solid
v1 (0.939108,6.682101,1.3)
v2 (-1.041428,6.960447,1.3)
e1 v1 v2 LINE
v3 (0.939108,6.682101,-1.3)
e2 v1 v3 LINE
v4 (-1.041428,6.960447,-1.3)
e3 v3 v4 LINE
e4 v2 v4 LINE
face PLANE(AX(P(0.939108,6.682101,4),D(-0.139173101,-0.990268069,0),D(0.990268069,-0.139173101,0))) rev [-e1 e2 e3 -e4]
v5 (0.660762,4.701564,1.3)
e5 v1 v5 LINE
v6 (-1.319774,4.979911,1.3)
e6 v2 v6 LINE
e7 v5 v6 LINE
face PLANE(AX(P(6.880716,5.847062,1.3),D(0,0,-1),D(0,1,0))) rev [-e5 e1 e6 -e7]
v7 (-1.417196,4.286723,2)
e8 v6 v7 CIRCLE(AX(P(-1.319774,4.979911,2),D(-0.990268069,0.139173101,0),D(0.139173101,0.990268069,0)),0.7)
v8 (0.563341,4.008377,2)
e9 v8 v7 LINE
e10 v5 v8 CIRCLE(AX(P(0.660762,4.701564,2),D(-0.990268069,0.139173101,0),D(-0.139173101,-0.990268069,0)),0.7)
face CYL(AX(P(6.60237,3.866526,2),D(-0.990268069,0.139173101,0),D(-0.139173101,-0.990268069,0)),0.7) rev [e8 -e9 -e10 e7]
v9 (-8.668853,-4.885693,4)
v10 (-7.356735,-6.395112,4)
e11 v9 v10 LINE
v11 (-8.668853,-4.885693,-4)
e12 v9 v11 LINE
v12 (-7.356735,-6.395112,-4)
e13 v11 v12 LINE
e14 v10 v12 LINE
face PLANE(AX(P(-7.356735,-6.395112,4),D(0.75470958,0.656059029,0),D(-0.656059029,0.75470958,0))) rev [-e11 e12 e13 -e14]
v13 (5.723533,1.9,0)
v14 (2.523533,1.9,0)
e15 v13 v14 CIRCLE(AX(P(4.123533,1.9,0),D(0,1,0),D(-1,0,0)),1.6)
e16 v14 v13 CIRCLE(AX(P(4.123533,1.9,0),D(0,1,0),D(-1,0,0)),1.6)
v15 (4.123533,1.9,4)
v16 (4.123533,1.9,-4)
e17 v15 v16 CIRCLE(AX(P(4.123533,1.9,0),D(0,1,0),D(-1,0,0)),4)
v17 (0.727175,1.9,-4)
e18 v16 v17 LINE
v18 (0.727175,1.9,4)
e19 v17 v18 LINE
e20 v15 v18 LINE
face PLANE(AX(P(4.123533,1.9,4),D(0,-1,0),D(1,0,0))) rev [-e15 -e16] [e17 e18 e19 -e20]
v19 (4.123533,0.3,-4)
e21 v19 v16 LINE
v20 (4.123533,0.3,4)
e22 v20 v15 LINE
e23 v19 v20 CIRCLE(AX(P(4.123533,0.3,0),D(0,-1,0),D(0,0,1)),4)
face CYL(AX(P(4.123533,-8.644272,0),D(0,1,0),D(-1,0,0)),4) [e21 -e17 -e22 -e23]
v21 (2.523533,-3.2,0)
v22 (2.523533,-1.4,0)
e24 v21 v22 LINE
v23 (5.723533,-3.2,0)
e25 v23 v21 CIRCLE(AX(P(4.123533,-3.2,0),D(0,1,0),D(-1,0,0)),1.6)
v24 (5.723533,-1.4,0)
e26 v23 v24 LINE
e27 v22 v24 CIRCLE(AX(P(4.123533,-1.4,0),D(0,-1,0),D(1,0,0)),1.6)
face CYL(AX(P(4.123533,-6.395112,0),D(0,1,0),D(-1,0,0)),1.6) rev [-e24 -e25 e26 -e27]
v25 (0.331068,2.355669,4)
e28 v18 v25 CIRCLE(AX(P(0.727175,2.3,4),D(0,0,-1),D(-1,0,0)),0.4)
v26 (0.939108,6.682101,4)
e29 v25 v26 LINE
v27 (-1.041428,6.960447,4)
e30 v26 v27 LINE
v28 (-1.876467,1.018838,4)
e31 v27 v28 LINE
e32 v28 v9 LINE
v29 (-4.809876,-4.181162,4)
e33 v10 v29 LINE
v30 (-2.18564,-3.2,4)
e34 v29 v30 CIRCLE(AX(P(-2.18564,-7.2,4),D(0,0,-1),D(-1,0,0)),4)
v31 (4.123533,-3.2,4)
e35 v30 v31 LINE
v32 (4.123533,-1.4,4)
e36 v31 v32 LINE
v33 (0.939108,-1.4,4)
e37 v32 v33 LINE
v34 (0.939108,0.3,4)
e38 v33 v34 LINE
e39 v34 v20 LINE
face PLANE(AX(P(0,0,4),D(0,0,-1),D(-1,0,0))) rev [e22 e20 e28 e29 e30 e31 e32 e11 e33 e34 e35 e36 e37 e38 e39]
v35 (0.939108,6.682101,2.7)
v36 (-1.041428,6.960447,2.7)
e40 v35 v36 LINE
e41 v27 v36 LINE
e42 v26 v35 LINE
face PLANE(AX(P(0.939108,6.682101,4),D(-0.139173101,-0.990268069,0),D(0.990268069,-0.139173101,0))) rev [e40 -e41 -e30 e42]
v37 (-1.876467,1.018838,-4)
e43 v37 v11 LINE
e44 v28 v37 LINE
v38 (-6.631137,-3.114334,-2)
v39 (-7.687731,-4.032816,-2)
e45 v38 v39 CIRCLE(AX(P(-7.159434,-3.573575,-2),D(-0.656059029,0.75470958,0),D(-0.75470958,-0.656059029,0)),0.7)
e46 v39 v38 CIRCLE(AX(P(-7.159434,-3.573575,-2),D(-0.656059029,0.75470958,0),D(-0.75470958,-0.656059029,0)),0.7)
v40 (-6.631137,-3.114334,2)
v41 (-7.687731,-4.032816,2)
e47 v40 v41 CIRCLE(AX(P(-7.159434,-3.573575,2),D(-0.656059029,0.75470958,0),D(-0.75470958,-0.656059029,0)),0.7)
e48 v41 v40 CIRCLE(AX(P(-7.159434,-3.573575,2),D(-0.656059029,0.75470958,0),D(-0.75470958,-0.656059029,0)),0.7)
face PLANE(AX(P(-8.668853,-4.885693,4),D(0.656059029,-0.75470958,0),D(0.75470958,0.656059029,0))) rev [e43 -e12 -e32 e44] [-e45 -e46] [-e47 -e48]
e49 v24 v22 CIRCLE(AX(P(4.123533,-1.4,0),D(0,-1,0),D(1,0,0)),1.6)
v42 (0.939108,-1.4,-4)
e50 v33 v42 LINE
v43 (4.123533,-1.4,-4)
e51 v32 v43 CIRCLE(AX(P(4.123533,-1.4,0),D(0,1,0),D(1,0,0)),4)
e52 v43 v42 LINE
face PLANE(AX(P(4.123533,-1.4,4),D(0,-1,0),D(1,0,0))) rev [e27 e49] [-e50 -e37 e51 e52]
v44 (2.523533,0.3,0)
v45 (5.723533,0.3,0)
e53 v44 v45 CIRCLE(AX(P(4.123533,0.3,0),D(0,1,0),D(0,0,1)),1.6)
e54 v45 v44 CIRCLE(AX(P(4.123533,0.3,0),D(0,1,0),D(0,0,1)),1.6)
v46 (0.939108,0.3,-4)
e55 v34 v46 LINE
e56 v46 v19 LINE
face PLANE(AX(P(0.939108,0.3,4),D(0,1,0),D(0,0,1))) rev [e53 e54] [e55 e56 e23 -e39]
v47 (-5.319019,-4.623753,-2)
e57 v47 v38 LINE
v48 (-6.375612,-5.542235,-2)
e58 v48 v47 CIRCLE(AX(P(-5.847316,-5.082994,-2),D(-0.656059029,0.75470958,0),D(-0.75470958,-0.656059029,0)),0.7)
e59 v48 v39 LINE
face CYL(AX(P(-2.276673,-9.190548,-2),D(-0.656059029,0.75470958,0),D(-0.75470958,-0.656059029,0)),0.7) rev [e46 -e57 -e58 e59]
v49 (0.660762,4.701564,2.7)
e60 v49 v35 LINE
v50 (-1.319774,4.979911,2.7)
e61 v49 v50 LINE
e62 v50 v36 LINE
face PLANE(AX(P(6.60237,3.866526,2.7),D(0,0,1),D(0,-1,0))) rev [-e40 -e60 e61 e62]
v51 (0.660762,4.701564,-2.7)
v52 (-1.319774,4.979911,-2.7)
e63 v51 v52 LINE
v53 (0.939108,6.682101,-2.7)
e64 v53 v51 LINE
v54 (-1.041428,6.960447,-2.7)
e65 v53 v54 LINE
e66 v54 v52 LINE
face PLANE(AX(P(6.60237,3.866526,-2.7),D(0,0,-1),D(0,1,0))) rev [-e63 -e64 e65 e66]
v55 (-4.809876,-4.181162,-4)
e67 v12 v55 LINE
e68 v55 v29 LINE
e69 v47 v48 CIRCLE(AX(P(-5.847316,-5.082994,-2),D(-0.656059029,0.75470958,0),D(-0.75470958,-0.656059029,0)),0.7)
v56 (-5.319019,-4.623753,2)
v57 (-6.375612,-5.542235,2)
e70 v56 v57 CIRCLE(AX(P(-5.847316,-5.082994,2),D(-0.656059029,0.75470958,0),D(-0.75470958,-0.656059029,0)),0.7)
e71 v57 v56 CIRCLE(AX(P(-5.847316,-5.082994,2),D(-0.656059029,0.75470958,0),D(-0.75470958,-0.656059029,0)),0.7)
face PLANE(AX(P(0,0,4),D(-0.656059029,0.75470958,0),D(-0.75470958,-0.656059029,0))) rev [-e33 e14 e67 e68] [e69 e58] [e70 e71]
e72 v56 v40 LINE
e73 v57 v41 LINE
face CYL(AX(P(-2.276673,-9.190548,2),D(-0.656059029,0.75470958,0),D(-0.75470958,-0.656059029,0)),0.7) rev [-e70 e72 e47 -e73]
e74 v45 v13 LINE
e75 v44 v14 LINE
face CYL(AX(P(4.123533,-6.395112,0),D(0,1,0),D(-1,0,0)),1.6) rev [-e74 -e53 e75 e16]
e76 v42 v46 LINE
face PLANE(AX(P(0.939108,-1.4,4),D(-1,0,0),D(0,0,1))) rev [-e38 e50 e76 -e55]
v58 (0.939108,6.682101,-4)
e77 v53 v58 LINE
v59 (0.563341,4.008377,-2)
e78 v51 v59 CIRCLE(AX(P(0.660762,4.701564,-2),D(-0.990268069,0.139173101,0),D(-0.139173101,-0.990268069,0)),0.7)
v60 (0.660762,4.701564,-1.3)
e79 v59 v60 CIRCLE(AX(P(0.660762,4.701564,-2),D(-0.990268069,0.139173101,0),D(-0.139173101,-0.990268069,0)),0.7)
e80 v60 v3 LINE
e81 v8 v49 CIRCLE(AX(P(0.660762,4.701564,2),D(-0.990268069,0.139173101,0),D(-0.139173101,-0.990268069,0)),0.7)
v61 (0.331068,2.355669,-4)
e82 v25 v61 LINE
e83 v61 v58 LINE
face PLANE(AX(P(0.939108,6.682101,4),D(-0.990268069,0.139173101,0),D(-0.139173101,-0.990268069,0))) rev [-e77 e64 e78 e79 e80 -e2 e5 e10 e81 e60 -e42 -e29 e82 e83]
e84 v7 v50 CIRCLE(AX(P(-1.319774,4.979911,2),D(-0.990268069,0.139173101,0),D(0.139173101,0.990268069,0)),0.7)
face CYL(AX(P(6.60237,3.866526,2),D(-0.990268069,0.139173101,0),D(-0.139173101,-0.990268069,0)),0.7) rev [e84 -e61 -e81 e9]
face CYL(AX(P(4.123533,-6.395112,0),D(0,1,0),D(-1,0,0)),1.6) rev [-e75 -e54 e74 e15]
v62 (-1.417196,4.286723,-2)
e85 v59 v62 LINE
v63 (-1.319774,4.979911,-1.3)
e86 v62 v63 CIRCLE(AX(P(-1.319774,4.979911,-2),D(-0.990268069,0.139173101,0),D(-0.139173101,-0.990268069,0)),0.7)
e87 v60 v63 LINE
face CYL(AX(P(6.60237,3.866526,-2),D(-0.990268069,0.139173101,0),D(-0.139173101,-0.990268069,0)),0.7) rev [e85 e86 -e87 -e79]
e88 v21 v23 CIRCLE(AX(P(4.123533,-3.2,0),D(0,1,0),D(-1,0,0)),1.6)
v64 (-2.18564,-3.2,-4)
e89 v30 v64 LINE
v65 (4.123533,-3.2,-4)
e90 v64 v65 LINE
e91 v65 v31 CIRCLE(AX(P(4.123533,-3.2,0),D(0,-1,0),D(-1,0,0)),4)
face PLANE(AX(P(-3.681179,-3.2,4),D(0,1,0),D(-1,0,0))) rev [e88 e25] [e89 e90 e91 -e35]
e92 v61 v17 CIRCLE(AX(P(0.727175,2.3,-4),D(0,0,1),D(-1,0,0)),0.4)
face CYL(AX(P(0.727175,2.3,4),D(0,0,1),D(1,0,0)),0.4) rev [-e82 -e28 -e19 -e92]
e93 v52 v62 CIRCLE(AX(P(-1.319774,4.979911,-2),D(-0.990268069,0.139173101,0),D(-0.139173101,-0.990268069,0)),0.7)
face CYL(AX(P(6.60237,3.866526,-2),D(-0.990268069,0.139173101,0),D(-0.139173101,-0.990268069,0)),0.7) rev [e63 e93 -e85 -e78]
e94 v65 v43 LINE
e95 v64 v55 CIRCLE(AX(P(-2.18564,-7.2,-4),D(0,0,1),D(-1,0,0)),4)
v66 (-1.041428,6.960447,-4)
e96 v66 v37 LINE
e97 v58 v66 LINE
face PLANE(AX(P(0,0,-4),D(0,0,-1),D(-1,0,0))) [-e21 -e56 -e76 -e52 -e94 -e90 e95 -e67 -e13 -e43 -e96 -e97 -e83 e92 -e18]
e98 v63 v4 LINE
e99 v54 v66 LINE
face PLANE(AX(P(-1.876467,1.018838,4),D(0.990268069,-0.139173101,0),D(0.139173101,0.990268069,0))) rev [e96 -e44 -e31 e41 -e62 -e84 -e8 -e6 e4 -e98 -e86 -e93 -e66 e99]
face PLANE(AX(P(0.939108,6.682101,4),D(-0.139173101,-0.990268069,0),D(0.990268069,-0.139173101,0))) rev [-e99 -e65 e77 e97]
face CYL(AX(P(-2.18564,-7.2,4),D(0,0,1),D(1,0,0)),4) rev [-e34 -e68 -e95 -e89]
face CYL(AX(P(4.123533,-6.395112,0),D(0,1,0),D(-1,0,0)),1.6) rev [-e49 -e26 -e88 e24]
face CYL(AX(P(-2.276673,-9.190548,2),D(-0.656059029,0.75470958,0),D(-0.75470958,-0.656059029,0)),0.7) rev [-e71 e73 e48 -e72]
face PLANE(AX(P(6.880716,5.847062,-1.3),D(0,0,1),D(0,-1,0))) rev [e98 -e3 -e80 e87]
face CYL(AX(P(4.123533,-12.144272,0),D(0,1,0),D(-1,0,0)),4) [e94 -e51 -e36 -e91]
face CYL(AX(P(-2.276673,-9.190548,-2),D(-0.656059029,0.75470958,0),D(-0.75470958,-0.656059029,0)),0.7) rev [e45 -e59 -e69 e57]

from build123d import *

# Parameters (mm, degrees)
BASE_ARM_8MM_DEPTH   = 4
FINGER_SLOTS_DEPTH   = 8
SIDE_SLOT_PROFILE_R  = 0.7
SIDE_SLOT_DEPTH      = 12.515344682
CLEVIS_LUG_8MM_DEPTH = 4
LUG_END_ROUND_R4_R   = 4
EDGE_FILLET_R0_4_R   = 0.4
LUG_FILL_BOSS_DEPTH  = 1.8
LUG_BLEND_BOSS_DEPTH = 1.6
PIN_HOLE_PROFILE_R   = 1.6
PIN_HOLE_3_2_DEPTH   = 13.647446253


with BuildPart() as part:
    # Base Arm Profile → Base Arm 8mm (new, symmetric)
    with BuildSketch(Plane.XY):
        Polygon((0, 0), (-7.356734921, -6.3951121), (-8.668852979, -4.88569294), (-1.876466757, 1.018838321), (-1.041428151, 6.960446733), (0.939107986, 6.682100531), align=None)
    extrude(amount=BASE_ARM_8MM_DEPTH, both=True)

    # Finger Slots Profile → Finger Slots (cut)
    with BuildSketch(Plane(origin=(-1.980536137, 0.278346202, 0), x_dir=(0, 0, 1), z_dir=(-0.9902680687415697, 0.13917310096006985, 0))):
        with BuildLine():
            Line((-2.7, 4.747769359), (-2.7, 6.747769359))
            Line((-2.7, 6.747769359), (-1.3, 6.747769359))
            Line((-1.3, 6.747769359), (-1.3, 4.747769359))
            ThreePointArc((-1.3, 4.747769359), (-2, 4.047769359), (-2.7, 4.747769359))
        make_face()
        with BuildLine():
            Line((1.3, 6.747769359), (1.3, 4.747769359))
            ThreePointArc((1.3, 4.747769359), (2, 4.047769359), (2.7, 4.747769359))
            Line((2.7, 4.747769359), (2.7, 6.747769359))
            Line((2.7, 6.747769359), (1.3, 6.747769359))
        make_face()
    extrude(amount=-FINGER_SLOTS_DEPTH, mode=Mode.SUBTRACT)

    # Side Slot Profile → Side Slot (cut, through all)
    with BuildSketch(Plane(origin=(-1.312118058, 1.50941916, 0), x_dir=(0.7547095802227755, 0.6560590289905035, 0), z_dir=(-0.6560590289905035, 0.7547095802227755, 0))):
        with Locations(Location((-7.747769359, -2, 0), (0, 0, 180))):
            Circle(SIDE_SLOT_PROFILE_R)
        with Locations(Location((-7.747769359, 2, 0), (0, 0, 180))):
            Circle(SIDE_SLOT_PROFILE_R)
    extrude(amount=-SIDE_SLOT_DEPTH, mode=Mode.SUBTRACT)

    # Clevis Lug Profile → Clevis Lug 8mm (add, symmetric)
    with BuildSketch(Plane.XY):
        Polygon((-3.681178903, -3.2), (4.123533243, -3.2), (4.123533243, -1.4), (0.939107986, -1.4), (0.939107986, 0.3), (4.123533243, 0.3), (4.123533243, 1.9), (0.267027586, 1.9), (0, 0), align=None)
    extrude(amount=CLEVIS_LUG_8MM_DEPTH, both=True)

    # Lug End Round R4
    lug_end_round_r4_edges = [part.edges().sort_by_distance(p)[0] for p in [
        (-3.681178903, -3.2, 0),
    ]]
    fillet(lug_end_round_r4_edges, radius=LUG_END_ROUND_R4_R)

    # Edge Fillet R0.4
    edge_fillet_r0_4_edges = [part.edges().sort_by_distance(p)[0] for p in [
        (0.267027586, 1.9, 0),
    ]]
    fillet(edge_fillet_r0_4_edges, radius=EDGE_FILLET_R0_4_R)

    # Lug Fill Boss Profile → Lug Fill Boss (add)
    with BuildSketch(Plane(origin=(0, -1.4, 0), x_dir=(1, 0, 0), z_dir=(0, 1, 0))):
        with BuildLine():
            Line((4.123533243, 4), (4.123533243, -4))
            ThreePointArc((4.123533243, -4), (8.123533243, 0), (4.123533243, 4))
        make_face()
    extrude(amount=-LUG_FILL_BOSS_DEPTH)

    # Lug Blend Boss Profile → Lug Blend Boss (add)
    with BuildSketch(Plane(origin=(0, 1.9, 0), x_dir=(1, 0, 0), z_dir=(0, 1, 0))):
        with BuildLine():
            Line((4.123533243, 4), (4.123533243, -4))
            ThreePointArc((4.123533243, -4), (8.123533243, 0), (4.123533243, 4))
        make_face()
    extrude(amount=-LUG_BLEND_BOSS_DEPTH)

    # Pin Hole Profile → Pin Hole Ø3.2 (cut, through all)
    with BuildSketch(Plane(origin=(0, 1.9, 0), x_dir=(1, 0, 0), z_dir=(0, 1, 0))):
        with Locations(Location((4.123533243, 0, 0), (0, 0, 180))):
            Circle(PIN_HOLE_PROFILE_R)
    extrude(amount=-PIN_HOLE_3_2_DEPTH, mode=Mode.SUBTRACT)


solid = part.part
